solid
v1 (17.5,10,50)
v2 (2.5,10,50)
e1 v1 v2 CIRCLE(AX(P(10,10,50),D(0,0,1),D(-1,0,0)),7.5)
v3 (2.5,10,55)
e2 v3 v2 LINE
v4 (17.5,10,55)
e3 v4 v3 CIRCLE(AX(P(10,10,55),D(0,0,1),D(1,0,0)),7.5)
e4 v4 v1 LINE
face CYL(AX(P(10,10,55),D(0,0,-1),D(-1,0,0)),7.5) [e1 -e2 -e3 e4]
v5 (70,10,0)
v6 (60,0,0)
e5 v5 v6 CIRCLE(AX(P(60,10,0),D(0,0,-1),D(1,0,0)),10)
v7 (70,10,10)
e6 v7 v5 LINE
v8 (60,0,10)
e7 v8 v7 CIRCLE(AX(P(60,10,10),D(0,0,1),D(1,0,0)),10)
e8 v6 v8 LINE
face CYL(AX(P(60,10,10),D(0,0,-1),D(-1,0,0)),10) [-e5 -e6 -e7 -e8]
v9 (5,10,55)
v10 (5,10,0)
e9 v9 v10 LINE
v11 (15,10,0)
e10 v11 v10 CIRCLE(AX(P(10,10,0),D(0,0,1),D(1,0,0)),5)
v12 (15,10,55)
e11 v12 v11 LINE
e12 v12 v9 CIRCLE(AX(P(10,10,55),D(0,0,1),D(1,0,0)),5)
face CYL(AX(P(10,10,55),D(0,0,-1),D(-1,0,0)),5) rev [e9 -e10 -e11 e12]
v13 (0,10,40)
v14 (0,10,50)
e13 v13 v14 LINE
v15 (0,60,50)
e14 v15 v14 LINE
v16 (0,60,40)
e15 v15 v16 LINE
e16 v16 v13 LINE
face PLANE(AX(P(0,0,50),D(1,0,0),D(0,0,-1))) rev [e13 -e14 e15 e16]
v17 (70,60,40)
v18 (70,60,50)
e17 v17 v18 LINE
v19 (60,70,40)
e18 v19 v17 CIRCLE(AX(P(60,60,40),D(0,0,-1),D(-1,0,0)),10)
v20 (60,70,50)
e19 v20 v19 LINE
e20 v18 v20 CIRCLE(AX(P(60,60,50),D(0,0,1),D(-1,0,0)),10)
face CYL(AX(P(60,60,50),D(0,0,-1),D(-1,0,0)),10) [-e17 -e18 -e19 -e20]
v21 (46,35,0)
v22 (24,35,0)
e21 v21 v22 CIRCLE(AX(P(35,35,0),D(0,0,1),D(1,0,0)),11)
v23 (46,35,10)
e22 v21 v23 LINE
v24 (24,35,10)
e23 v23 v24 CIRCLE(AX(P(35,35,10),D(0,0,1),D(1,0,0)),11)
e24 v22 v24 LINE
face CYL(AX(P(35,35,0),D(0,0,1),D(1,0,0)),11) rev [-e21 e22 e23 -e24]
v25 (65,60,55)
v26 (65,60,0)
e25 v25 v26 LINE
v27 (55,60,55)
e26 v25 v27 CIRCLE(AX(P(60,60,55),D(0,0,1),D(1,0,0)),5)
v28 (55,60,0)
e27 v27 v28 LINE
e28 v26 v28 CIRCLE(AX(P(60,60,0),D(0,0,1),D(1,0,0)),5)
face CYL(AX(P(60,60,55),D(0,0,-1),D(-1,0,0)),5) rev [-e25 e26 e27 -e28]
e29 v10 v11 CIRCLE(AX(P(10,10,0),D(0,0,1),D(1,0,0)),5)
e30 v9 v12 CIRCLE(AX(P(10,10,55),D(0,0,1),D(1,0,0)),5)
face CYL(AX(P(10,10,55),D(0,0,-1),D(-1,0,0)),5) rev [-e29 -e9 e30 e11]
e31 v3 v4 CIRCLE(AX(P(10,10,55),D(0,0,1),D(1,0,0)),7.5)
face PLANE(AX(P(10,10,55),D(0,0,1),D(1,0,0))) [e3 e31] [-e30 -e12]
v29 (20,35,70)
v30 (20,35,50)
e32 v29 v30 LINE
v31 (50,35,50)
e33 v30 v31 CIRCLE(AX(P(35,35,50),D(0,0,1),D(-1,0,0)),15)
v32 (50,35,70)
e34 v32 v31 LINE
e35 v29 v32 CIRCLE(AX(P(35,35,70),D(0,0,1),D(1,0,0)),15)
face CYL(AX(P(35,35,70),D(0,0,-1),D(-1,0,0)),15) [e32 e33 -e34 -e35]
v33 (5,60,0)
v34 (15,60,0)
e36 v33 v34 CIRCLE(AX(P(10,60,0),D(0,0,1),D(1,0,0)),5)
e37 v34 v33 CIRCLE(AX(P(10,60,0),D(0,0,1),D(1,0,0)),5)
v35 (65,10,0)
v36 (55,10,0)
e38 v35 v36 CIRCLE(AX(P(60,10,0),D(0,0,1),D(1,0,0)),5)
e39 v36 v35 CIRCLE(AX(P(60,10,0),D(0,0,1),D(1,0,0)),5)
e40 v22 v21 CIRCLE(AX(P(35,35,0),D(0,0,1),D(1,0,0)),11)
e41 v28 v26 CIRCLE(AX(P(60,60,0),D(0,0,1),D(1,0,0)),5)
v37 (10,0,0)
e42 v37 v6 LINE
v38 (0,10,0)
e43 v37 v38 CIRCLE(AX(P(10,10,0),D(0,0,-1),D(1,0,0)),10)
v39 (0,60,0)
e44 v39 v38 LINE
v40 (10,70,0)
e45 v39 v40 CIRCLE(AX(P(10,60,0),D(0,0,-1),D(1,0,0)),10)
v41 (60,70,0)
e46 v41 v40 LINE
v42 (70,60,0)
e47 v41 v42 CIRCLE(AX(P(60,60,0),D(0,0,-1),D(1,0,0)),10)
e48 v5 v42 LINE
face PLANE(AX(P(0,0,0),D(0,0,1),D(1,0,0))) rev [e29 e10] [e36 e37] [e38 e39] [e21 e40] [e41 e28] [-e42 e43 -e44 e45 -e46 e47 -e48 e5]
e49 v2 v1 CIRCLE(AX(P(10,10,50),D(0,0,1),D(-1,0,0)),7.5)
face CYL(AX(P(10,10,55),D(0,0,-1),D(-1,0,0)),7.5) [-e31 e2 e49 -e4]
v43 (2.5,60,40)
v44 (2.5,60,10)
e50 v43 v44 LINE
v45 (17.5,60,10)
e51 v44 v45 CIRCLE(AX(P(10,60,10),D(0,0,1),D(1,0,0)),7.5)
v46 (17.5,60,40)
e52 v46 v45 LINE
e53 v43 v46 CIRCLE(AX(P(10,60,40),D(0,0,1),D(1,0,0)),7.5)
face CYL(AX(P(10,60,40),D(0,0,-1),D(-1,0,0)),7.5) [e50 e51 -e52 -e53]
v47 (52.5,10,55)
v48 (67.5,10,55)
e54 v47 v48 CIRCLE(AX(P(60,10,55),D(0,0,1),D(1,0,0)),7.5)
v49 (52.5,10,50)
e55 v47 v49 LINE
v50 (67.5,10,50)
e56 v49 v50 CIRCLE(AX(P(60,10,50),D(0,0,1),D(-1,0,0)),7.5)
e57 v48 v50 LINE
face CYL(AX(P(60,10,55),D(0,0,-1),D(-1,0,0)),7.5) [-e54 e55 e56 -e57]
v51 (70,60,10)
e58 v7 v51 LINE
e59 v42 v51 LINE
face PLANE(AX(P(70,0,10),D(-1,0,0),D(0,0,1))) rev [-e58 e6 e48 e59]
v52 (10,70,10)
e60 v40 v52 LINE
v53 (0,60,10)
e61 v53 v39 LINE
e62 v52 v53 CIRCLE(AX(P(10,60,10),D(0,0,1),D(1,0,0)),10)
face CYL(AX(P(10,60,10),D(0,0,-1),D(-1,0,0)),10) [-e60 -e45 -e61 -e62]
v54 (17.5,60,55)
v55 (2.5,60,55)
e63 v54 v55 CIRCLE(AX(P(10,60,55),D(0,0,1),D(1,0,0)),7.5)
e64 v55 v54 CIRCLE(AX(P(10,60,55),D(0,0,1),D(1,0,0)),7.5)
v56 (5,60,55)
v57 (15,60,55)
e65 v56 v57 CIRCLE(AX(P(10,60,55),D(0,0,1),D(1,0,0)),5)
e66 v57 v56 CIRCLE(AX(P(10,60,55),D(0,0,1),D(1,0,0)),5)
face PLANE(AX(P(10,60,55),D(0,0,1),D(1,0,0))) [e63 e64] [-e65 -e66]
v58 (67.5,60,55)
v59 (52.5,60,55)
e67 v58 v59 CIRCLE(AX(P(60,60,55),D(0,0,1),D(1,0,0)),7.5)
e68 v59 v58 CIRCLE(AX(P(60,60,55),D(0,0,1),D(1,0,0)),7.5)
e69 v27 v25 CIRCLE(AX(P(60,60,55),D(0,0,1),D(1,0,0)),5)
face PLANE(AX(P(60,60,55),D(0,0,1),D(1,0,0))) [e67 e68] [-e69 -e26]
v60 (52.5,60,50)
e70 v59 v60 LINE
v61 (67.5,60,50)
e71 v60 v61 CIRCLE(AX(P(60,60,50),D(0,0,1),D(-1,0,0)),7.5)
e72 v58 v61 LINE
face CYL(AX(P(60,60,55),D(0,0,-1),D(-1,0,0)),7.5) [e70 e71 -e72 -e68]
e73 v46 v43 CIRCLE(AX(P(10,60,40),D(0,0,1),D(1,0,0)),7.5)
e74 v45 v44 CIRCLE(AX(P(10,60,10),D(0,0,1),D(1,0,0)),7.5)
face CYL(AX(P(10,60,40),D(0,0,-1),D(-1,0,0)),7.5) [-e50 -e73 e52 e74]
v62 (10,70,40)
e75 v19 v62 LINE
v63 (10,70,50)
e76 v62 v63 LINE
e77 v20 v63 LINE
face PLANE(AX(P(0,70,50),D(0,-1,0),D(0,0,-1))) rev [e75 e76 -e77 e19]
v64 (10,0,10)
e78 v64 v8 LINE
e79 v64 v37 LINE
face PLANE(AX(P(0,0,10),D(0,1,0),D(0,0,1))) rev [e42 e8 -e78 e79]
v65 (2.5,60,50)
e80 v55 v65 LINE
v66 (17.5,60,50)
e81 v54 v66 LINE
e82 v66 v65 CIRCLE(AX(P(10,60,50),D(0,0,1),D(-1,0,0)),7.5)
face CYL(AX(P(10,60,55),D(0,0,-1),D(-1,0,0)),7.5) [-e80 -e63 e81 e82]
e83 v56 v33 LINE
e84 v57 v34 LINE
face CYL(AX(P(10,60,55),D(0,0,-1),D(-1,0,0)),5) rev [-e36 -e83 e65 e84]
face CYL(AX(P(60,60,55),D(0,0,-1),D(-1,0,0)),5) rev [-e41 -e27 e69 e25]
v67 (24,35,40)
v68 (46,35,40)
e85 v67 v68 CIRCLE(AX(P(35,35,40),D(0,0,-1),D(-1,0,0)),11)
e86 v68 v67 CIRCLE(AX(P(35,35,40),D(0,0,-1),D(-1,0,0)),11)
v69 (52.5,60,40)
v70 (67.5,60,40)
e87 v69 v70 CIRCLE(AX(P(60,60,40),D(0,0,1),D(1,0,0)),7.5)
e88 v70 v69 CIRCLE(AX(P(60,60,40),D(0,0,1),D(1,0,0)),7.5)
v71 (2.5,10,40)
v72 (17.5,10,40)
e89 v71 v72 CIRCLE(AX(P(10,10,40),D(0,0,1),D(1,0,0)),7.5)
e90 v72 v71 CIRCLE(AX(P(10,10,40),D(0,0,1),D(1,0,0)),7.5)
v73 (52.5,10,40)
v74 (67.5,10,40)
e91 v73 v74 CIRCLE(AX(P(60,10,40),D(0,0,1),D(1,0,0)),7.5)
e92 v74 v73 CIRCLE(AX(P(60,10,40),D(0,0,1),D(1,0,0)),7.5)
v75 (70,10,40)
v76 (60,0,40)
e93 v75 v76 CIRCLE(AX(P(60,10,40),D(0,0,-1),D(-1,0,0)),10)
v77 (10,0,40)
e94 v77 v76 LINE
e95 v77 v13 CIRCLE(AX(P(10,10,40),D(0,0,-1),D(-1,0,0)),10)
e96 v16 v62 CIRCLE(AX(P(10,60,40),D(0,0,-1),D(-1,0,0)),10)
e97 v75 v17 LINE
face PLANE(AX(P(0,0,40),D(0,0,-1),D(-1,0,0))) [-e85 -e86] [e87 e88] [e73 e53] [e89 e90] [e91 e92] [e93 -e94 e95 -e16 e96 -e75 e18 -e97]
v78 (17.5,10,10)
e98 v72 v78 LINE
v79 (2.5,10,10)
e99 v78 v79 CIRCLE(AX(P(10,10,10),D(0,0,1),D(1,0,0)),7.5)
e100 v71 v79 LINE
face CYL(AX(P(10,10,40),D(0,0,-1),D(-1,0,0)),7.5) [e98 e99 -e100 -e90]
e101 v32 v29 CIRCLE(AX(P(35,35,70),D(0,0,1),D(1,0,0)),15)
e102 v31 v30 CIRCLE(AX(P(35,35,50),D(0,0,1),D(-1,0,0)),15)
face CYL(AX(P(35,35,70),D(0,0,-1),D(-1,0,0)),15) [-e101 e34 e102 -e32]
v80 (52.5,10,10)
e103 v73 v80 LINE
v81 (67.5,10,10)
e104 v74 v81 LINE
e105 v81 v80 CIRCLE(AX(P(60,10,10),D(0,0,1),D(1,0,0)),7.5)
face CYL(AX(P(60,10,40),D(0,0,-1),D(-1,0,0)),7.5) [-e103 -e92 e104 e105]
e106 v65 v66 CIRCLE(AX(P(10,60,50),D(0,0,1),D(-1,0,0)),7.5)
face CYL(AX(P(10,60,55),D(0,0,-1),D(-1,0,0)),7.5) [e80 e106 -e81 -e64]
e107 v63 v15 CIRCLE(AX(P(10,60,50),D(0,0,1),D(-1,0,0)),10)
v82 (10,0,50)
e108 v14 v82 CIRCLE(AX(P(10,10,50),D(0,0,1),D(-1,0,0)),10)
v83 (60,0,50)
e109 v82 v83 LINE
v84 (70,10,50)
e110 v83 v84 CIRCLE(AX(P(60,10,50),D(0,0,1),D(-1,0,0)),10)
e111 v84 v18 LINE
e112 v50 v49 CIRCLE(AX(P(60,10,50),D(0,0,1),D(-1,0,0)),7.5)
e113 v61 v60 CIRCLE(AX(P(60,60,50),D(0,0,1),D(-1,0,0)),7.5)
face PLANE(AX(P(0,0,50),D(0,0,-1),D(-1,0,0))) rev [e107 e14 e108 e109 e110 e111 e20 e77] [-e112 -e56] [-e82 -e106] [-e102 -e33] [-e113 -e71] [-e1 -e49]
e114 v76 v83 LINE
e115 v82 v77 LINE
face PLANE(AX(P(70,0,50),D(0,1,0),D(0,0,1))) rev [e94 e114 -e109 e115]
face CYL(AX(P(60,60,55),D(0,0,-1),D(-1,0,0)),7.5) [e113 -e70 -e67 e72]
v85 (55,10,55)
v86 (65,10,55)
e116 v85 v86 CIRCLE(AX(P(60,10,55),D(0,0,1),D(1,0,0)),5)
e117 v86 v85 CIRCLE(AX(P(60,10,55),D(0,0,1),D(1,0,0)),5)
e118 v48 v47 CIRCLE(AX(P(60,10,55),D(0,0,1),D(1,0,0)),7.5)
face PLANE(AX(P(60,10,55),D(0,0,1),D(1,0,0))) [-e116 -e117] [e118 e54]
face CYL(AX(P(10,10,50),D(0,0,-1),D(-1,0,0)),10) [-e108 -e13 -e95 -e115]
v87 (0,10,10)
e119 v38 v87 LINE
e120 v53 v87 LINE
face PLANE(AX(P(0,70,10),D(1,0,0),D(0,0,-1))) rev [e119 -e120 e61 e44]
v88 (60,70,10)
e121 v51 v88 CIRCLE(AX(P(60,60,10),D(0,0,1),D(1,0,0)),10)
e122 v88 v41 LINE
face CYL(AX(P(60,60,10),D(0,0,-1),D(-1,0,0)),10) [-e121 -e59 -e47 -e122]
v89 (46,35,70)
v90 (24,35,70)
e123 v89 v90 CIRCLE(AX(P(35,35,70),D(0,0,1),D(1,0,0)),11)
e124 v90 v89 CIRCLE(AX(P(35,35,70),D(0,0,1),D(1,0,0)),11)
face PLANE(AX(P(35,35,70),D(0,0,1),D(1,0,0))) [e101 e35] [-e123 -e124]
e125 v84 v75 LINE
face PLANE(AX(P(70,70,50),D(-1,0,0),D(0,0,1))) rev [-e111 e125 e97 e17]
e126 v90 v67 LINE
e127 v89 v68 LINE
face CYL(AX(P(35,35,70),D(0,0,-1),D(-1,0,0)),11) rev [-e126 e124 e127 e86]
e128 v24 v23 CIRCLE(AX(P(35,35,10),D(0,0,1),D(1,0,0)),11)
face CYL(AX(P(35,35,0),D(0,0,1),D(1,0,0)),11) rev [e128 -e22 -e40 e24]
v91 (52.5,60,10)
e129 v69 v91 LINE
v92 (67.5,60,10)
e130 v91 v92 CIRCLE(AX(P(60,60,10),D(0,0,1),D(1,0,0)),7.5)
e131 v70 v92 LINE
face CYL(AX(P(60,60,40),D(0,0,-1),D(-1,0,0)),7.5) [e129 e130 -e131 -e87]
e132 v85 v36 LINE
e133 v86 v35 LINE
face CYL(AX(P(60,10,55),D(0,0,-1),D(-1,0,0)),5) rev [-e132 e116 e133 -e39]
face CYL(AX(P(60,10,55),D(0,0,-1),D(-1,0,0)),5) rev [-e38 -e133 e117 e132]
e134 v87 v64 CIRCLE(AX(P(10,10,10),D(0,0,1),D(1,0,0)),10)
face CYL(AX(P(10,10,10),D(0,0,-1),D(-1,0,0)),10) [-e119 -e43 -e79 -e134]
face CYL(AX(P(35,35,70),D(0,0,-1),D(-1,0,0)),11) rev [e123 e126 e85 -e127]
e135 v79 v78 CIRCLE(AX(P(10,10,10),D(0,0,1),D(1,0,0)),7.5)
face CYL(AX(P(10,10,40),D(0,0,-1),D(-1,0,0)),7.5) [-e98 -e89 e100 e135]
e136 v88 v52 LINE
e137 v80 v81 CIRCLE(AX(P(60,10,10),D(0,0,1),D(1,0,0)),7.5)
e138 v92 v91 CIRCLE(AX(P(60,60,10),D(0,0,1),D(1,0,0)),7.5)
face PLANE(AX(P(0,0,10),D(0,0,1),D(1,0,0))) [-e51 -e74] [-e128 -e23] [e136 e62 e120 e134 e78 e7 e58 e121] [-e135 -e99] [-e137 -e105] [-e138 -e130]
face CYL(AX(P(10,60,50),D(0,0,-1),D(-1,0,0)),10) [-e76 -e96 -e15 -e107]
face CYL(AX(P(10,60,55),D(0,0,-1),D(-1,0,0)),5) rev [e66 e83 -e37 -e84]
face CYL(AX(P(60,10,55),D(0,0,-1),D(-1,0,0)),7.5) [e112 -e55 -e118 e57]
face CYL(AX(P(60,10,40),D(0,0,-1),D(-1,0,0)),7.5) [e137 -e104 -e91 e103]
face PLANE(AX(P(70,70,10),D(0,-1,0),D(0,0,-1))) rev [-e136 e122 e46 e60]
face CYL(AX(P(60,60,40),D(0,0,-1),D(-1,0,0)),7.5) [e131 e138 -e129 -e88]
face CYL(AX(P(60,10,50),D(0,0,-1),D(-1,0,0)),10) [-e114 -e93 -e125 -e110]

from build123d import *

# Parameters (mm, degrees)
BASE_PLATE_SKETCH_W             = 70
BASE_PLATE_SKETCH_H             = 70
BASE_PLATE_DEPTH                = 10
CORNER_POSTS_SKETCH_R           = 7.5
CORNER_POSTS_4X_DEPTH           = 30
TOP_PLATE_SKETCH_W              = 70
TOP_PLATE_SKETCH_H              = 70
TOP_PLATE_DEPTH                 = 10
POST_BOSSES_SKETCH_R            = 7.5
POST_BOSSES_SKETCH_R_2          = 5
POST_BOSSES_4X_DEPTH            = 5
CENTRE_BOSS_SKETCH_R            = 15
CENTRE_BOSS_SKETCH_R_2          = 11
CENTRE_BOSS_30_DEPTH            = 20
CENTRE_BORE_SKETCH_R            = 11
CENTRE_BORE_CUT_DEPTH           = 111.905365064
POST_HOLES_SKETCH_R             = 5
POST_HOLES_4X_DEPTH             = 111.905365064
TOP_PLATE_CORNER_FILLETS_R10_R  = 10
BASE_PLATE_CORNER_FILLETS_R10_R = 10


with BuildPart() as part:
    # Base Plate Sketch → Base Plate (new body)
    with BuildSketch(Plane.XY):
        with Locations((35, 35)):
            Rectangle(BASE_PLATE_SKETCH_W, BASE_PLATE_SKETCH_H)
    extrude(amount=BASE_PLATE_DEPTH)

    # Corner Posts Sketch → Corner Posts 4x (add)
    with BuildSketch(Plane.XY.offset(10)):
        with Locations((10, 10)):
            Circle(CORNER_POSTS_SKETCH_R)
        with Locations((60, 10)):
            Circle(CORNER_POSTS_SKETCH_R)
        with Locations((60, 60)):
            Circle(CORNER_POSTS_SKETCH_R)
        with Locations((10, 60)):
            Circle(CORNER_POSTS_SKETCH_R)
    extrude(amount=CORNER_POSTS_4X_DEPTH)

    # Top Plate Sketch → Top Plate (add)
    with BuildSketch(Plane.XY.offset(40)):
        with Locations((35, 35)):
            Rectangle(TOP_PLATE_SKETCH_W, TOP_PLATE_SKETCH_H)
    extrude(amount=TOP_PLATE_DEPTH)

    # Post Bosses Sketch → Post Bosses 4x (add)
    # profile 1 of 4: a face of its own
    with BuildSketch(Plane.XY.offset(50)):
        with Locations((10, 60)):
            Circle(POST_BOSSES_SKETCH_R)
        with Locations((10, 60)):
            Circle(POST_BOSSES_SKETCH_R_2, mode=Mode.SUBTRACT)
    # profile 2 of 4: a face of its own
    with BuildSketch(Plane.XY.offset(50)):
        with Locations((60, 60)):
            Circle(POST_BOSSES_SKETCH_R)
        with Locations((60, 60)):
            Circle(POST_BOSSES_SKETCH_R_2, mode=Mode.SUBTRACT)
    # profile 3 of 4: a face of its own
    with BuildSketch(Plane.XY.offset(50)):
        with Locations((10, 10)):
            Circle(POST_BOSSES_SKETCH_R)
        with Locations((10, 10)):
            Circle(POST_BOSSES_SKETCH_R_2, mode=Mode.SUBTRACT)
    # profile 4 of 4: a face of its own
    with BuildSketch(Plane.XY.offset(50)):
        with Locations((60, 10)):
            Circle(POST_BOSSES_SKETCH_R)
        with Locations((60, 10)):
            Circle(POST_BOSSES_SKETCH_R_2, mode=Mode.SUBTRACT)
    extrude(amount=POST_BOSSES_4X_DEPTH)

    # Centre Boss Sketch → Centre Boss Ø30 (add)
    with BuildSketch(Plane.XY.offset(50)):
        with Locations(Location((35, 35, 0), (0, 0, 180))):
            Circle(CENTRE_BOSS_SKETCH_R)
        with Locations((35, 35)):
            Circle(CENTRE_BOSS_SKETCH_R_2, mode=Mode.SUBTRACT)
    extrude(amount=CENTRE_BOSS_30_DEPTH)

    # Centre Bore Sketch → Centre Bore Cut (cut, through all)
    with BuildSketch(Plane.XY.offset(50)):
        with Locations(Location((35, 35, 0), (0, 0, 180))):
            Circle(CENTRE_BORE_SKETCH_R)
    extrude(amount=-CENTRE_BORE_CUT_DEPTH, mode=Mode.SUBTRACT)

    # Post Holes Sketch → Post Holes 4x (cut, through all)
    with BuildSketch(Plane.XY.offset(50)):
        with Locations((60, 60)):
            Circle(POST_HOLES_SKETCH_R)
        with Locations((10, 60)):
            Circle(POST_HOLES_SKETCH_R)
        with Locations((60, 10)):
            Circle(POST_HOLES_SKETCH_R)
        with Locations((10, 10)):
            Circle(POST_HOLES_SKETCH_R)
    extrude(amount=-POST_HOLES_4X_DEPTH, mode=Mode.SUBTRACT)

    # Top Plate Corner Fillets R10
    top_plate_corner_fillets_r10_edges = [part.edges().sort_by_distance(p)[0] for p in [
        (0, 70, 45),
        (0, 0, 45),
        (70, 0, 45),
        (70, 70, 45),
    ]]
    fillet(top_plate_corner_fillets_r10_edges, radius=TOP_PLATE_CORNER_FILLETS_R10_R)

    # Base Plate Corner Fillets R10
    base_plate_corner_fillets_r10_edges = [part.edges().sort_by_distance(p)[0] for p in [
        (0, 70, 5),
        (70, 70, 5),
        (70, 0, 5),
        (0, 0, 5),
    ]]
    fillet(base_plate_corner_fillets_r10_edges, radius=BASE_PLATE_CORNER_FILLETS_R10_R)


solid = part.part
